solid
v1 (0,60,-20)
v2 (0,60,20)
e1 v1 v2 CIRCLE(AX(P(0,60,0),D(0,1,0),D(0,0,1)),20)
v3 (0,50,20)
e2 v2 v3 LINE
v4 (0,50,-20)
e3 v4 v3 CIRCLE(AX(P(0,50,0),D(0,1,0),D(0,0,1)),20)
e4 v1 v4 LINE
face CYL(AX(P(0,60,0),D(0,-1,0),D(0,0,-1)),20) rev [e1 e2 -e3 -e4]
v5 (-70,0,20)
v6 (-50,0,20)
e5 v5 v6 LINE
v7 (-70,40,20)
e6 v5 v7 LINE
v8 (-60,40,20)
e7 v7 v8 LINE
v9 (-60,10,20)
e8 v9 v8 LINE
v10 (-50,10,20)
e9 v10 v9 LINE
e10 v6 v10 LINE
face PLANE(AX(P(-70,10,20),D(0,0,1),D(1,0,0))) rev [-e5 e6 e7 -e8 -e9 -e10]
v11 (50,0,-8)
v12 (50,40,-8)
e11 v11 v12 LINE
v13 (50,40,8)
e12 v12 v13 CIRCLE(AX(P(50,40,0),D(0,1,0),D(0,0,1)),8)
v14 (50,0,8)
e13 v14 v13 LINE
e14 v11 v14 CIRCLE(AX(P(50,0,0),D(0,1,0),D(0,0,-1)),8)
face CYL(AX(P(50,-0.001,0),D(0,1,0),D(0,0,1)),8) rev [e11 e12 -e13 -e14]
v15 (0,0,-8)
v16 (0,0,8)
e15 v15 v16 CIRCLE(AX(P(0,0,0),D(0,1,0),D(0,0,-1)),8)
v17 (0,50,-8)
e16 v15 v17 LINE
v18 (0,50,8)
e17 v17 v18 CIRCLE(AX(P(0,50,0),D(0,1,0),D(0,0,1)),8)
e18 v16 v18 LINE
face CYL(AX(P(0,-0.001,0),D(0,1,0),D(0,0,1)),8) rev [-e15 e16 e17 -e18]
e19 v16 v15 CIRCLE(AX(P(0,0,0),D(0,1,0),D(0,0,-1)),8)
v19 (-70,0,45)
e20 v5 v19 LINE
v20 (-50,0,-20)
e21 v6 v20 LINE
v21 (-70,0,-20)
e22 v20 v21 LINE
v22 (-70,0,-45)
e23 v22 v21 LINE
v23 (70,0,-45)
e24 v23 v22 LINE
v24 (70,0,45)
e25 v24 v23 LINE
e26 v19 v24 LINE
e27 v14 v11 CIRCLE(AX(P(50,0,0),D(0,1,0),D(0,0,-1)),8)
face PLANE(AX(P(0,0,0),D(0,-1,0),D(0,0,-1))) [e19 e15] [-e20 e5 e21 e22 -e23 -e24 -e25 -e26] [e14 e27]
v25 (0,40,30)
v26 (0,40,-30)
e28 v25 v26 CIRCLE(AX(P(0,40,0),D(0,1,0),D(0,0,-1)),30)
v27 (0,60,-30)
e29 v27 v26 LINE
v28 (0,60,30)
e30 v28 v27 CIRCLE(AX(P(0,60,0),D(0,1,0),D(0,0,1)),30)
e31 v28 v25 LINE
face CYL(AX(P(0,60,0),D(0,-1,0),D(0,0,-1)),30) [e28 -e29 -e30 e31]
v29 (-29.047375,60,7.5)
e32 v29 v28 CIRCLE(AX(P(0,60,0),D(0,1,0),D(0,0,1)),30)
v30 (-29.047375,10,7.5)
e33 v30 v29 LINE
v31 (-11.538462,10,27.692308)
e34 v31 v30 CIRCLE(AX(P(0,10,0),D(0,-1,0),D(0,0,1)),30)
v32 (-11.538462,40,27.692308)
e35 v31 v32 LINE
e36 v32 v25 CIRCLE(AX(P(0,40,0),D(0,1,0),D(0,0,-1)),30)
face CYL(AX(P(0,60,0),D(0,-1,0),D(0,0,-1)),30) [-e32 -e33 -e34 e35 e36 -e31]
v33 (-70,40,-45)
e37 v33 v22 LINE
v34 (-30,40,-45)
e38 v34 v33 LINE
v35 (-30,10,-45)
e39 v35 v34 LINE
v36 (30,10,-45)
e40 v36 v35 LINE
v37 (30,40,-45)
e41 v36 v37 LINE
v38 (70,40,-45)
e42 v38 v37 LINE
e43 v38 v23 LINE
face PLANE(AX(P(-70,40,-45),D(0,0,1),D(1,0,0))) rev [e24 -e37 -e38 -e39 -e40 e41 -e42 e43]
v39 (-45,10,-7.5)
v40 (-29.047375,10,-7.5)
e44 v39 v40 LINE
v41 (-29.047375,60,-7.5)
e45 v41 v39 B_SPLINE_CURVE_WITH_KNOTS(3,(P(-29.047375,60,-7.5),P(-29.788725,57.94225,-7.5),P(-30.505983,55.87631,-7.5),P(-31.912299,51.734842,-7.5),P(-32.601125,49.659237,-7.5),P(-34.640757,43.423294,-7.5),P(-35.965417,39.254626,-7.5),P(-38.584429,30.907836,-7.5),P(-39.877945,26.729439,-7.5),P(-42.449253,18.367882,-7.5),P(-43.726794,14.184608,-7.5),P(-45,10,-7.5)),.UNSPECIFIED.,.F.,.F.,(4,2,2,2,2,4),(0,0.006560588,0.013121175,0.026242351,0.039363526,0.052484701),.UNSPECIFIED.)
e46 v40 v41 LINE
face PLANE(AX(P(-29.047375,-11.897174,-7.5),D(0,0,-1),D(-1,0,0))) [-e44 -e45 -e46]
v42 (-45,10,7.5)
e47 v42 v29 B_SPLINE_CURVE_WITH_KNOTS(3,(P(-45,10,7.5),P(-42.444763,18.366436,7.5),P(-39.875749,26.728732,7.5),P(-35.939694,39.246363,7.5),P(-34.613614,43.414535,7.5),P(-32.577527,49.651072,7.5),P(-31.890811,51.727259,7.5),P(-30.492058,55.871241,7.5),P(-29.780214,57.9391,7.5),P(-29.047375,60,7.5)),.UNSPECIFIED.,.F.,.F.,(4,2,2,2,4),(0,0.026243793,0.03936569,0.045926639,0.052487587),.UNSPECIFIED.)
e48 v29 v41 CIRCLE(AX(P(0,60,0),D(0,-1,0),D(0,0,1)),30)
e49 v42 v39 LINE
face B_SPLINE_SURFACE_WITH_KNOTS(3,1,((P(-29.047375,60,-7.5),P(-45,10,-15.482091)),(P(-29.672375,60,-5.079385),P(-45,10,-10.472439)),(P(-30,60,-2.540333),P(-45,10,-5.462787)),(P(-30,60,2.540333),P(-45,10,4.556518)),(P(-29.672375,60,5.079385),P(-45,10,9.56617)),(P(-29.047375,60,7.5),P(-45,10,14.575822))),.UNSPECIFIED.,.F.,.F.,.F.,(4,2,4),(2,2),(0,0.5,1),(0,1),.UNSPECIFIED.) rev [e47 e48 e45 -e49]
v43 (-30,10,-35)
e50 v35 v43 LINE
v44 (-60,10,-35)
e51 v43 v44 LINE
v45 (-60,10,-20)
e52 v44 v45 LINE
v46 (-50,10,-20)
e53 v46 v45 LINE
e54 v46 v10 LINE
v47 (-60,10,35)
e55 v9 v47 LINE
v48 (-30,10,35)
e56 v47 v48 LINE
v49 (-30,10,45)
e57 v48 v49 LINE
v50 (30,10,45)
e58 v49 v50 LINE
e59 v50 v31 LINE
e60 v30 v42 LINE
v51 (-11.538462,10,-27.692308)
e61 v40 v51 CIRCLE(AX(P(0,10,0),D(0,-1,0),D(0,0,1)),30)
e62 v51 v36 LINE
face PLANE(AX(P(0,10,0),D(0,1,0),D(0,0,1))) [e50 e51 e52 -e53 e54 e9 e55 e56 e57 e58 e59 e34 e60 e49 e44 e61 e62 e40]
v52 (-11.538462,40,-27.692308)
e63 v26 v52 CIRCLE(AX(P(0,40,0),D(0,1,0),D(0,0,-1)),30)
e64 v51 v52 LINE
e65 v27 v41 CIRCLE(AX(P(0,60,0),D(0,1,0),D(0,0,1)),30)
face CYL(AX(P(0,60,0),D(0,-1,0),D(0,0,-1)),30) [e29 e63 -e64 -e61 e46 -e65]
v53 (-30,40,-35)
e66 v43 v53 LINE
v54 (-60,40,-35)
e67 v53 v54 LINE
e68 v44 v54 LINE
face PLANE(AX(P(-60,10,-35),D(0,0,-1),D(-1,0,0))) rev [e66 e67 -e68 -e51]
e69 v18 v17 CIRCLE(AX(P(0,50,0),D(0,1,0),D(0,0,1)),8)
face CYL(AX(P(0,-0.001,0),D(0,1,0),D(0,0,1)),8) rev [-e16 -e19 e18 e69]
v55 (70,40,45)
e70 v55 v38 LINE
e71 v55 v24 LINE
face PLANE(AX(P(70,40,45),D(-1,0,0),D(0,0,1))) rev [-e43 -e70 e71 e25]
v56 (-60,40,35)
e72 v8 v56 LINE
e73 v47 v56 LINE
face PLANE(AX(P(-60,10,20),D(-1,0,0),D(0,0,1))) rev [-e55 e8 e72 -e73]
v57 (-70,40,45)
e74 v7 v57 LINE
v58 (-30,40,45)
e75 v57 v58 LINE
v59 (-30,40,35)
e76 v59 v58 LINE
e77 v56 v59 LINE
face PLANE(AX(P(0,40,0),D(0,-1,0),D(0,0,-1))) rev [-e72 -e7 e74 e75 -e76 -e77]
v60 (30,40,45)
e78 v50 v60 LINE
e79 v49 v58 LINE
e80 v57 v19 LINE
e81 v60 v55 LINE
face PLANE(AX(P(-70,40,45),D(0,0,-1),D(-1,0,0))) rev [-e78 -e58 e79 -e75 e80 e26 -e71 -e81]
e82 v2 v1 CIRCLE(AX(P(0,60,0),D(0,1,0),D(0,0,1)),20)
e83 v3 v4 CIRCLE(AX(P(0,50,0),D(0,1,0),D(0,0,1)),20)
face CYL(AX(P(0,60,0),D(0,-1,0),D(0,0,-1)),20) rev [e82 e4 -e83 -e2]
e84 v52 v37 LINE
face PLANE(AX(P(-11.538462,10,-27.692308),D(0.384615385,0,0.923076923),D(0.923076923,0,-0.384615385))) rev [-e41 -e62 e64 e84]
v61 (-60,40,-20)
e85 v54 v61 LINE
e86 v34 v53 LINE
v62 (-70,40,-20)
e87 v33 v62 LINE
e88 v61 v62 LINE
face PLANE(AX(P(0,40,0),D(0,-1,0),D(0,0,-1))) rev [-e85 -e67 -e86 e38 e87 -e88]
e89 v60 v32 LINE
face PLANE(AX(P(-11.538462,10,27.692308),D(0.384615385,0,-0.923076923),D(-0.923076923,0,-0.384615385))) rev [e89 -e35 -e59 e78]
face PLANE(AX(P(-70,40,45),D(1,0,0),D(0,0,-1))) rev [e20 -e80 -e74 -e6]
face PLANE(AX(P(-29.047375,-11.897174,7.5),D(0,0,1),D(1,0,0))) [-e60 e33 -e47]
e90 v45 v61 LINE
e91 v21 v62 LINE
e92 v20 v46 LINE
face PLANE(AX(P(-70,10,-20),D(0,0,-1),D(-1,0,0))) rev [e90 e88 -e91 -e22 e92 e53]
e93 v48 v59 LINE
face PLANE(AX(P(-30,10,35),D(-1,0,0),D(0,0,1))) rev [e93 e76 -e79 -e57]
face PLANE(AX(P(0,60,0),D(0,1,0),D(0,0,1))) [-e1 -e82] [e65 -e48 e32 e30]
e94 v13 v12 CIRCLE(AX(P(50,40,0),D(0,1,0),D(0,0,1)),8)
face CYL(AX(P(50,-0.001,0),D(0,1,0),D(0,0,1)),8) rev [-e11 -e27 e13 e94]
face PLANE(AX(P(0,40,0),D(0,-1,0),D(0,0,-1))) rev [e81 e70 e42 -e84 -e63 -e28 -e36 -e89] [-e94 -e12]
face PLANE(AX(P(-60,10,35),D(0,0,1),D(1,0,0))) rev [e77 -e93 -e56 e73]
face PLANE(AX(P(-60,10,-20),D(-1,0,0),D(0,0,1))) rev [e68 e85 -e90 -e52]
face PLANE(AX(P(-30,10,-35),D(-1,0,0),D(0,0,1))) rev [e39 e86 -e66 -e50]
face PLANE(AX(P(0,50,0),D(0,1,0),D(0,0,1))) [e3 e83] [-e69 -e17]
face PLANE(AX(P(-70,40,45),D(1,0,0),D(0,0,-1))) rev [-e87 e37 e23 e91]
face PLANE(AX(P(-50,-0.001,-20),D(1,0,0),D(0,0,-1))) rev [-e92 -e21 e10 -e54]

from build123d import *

# Parameters (mm, degrees)
BASE_PLATE_SKETCH_W        = 140
BASE_PLATE_SKETCH_H        = 90
BASE_PLATE_DEPTH           = 40
GLAND_BOSS_SKETCH_R        = 30
GLAND_BOSS_SKETCH_R_2      = 20
GLAND_BOSS_DEPTH           = 60
FORK_START                 = -30
FORK_CUTOUT_DEPTH          = 30
BORE_AND_HOLE_CUT_REACH    = 94.331
BORE_AND_HOLE_CUT_SKETCH_R = 8
BORE_AND_HOLE_CUT_SKETCH_W = 20
BORE_AND_HOLE_CUT_SKETCH_H = 40
SUPPORT_WEB_SKETCH_W       = 15.952624903
SUPPORT_WEB_SKETCH_H       = 15
SUPPORT_WEB_DEPTH          = 50
LIP_SKETCH_R               = 20
LIP_SKETCH_R_2             = 8
LIP_10MM_DEPTH             = 10


with BuildPart() as part:
    # Base Plate Sketch → Base Plate (new body)
    with BuildSketch(Plane(origin=(0, 0, 0), x_dir=(1, 0, 0), z_dir=(0, 1, 0))):
        Rectangle(BASE_PLATE_SKETCH_W, BASE_PLATE_SKETCH_H)
    extrude(amount=BASE_PLATE_DEPTH)

    # Gland Boss Sketch → Gland Boss (add)
    with BuildSketch(Plane(origin=(0, 0, 0), x_dir=(1, 0, 0), z_dir=(0, 1, 0))):
        with Locations(Location((0, 0, 0), (0, 0, 90))):
            Circle(GLAND_BOSS_SKETCH_R)
        with Locations(Location((0, 0, 0), (0, 0, 90))):
            Circle(GLAND_BOSS_SKETCH_R_2, mode=Mode.SUBTRACT)
    extrude(amount=GLAND_BOSS_DEPTH)

    # Fork Cutout Sketch → Fork Cutout (cut)
    with BuildSketch(Plane(origin=(0, 40, 0), x_dir=(1, 0, 0), z_dir=(0, 1, 0)).offset(FORK_START)):
        with BuildLine():
            Line((-70, 20), (-60, 20))
            Line((-60, 20), (-60, 35))
            Line((-60, 35), (-30, 35))
            Line((-30, 35), (-30, 45))
            Line((-30, 45), (30, 45))
            Line((30, 45), (-11.538461538, 27.692307692))
            ThreePointArc((-11.538461538, 27.692307692), (-30, 0), (-11.538461538, -27.692307692))
            Line((-11.538461538, -27.692307692), (30, -45))
            Line((30, -45), (-30, -45))
            Line((-30, -45), (-30, -35))
            Line((-30, -35), (-60, -35))
            Line((-60, -35), (-60, -20))
            Line((-60, -20), (-70, -20))
            Line((-70, -20), (-70, 20))
        make_face()
    extrude(amount=FORK_CUTOUT_DEPTH, mode=Mode.SUBTRACT)

    # Bore and Hole Cut Sketch → Bore and Hole Cut (cut, up to next)
    with BuildSketch(Plane(origin=(0, 40, 0), x_dir=(1, 0, 0), z_dir=(0, 1, 0)), mode=Mode.PRIVATE) as bore_and_hole_cut_sk1:
        with Locations(Location((0, 0, 0), (0, 0, 270))):
            Circle(BORE_AND_HOLE_CUT_SKETCH_R)
    bore_and_hole_cut_tool1 = extrude(bore_and_hole_cut_sk1.sketch, amount=-BORE_AND_HOLE_CUT_REACH, mode=Mode.PRIVATE) & part.part
    # Bore and Hole Cut Sketch → Bore and Hole Cut (cut, up to next)
    with BuildSketch(Plane(origin=(0, 40, 0), x_dir=(1, 0, 0), z_dir=(0, 1, 0)), mode=Mode.PRIVATE) as bore_and_hole_cut_sk2:
        with Locations(Location((50, 0, 0), (0, 0, 270))):
            Circle(BORE_AND_HOLE_CUT_SKETCH_R)
    bore_and_hole_cut_tool2 = extrude(bore_and_hole_cut_sk2.sketch, amount=-BORE_AND_HOLE_CUT_REACH, mode=Mode.PRIVATE) & part.part
    # Bore and Hole Cut Sketch → Bore and Hole Cut (cut, up to next)
    with BuildSketch(Plane(origin=(0, 40, 0), x_dir=(1, 0, 0), z_dir=(0, 1, 0)), mode=Mode.PRIVATE) as bore_and_hole_cut_sk3:
        with Locations((-60, 0)):
            Rectangle(BORE_AND_HOLE_CUT_SKETCH_W, BORE_AND_HOLE_CUT_SKETCH_H)
    bore_and_hole_cut_tool3 = extrude(bore_and_hole_cut_sk3.sketch, amount=-BORE_AND_HOLE_CUT_REACH, mode=Mode.PRIVATE) & part.part
    add(bore_and_hole_cut_tool1.solids().sort_by_distance((0, 40, 0))[0], mode=Mode.SUBTRACT)
    add(bore_and_hole_cut_tool2.solids().sort_by_distance((50, 40, 0))[0], mode=Mode.SUBTRACT)
    add(bore_and_hole_cut_tool3.solids().sort_by_distance((-60, 40, 0))[0], mode=Mode.SUBTRACT)

    # Support Web Sketch → Support Web (add)
    with BuildSketch(Plane(origin=(0, 60, 0), x_dir=(1, 0, 0), z_dir=(0, 1, 0))):
        with Locations((-37.023687548, 0)):
            Rectangle(SUPPORT_WEB_SKETCH_W, SUPPORT_WEB_SKETCH_H)
    extrude(amount=-SUPPORT_WEB_DEPTH)

    # Tapered Cut Start Profil for Tapered Lof → Tapered Lofted Cut section 0
    with BuildSketch(Plane(origin=(0, 60, 0), x_dir=(1, 0, 0), z_dir=(0, 1, 0))):
        with BuildLine():
            Line((-29.047375097, 7.5), (-45, 7.5))
            Line((-45, 7.5), (-45, -7.5))
            Line((-45, -7.5), (-29.047375097, -7.5))
            # circular arc as an exact rational Bezier (weights 1, cos(half-angle), 1)
            Bezier((-29.047375097, -7.5), (-30.98386677, 0), (-29.047375097, 7.5), weights=[1, 0.968245837, 1])
        make_face()
    # Tapered Cut End Profile → Tapered Lofted Cut section 1
    with BuildSketch(Plane(origin=(0, 10, 0), x_dir=(1, 0, 0), z_dir=(0, 1, 0))):
        with BuildLine():
            Line((-50, 15.482090991), (-45, 15.482090991))
            Line((-45, 15.482090991), (-45, -14.57582225))
            Line((-45, -14.57582225), (-50, -14.57582225))
            Line((-50, -14.57582225), (-50, 15.482090991))
        make_face()
    loft(mode=Mode.SUBTRACT)

    # Lip Sketch → Lip 10mm (add)
    with BuildSketch(Plane(origin=(0, 40, 0), x_dir=(1, 0, 0), z_dir=(0, 1, 0))):
        with Locations(Location((0, 0, 0), (0, 0, 270))):
            Circle(LIP_SKETCH_R)
        with Locations(Location((0, 0, 0), (0, 0, 270))):
            Circle(LIP_SKETCH_R_2, mode=Mode.SUBTRACT)
    extrude(amount=LIP_10MM_DEPTH)


solid = part.part
